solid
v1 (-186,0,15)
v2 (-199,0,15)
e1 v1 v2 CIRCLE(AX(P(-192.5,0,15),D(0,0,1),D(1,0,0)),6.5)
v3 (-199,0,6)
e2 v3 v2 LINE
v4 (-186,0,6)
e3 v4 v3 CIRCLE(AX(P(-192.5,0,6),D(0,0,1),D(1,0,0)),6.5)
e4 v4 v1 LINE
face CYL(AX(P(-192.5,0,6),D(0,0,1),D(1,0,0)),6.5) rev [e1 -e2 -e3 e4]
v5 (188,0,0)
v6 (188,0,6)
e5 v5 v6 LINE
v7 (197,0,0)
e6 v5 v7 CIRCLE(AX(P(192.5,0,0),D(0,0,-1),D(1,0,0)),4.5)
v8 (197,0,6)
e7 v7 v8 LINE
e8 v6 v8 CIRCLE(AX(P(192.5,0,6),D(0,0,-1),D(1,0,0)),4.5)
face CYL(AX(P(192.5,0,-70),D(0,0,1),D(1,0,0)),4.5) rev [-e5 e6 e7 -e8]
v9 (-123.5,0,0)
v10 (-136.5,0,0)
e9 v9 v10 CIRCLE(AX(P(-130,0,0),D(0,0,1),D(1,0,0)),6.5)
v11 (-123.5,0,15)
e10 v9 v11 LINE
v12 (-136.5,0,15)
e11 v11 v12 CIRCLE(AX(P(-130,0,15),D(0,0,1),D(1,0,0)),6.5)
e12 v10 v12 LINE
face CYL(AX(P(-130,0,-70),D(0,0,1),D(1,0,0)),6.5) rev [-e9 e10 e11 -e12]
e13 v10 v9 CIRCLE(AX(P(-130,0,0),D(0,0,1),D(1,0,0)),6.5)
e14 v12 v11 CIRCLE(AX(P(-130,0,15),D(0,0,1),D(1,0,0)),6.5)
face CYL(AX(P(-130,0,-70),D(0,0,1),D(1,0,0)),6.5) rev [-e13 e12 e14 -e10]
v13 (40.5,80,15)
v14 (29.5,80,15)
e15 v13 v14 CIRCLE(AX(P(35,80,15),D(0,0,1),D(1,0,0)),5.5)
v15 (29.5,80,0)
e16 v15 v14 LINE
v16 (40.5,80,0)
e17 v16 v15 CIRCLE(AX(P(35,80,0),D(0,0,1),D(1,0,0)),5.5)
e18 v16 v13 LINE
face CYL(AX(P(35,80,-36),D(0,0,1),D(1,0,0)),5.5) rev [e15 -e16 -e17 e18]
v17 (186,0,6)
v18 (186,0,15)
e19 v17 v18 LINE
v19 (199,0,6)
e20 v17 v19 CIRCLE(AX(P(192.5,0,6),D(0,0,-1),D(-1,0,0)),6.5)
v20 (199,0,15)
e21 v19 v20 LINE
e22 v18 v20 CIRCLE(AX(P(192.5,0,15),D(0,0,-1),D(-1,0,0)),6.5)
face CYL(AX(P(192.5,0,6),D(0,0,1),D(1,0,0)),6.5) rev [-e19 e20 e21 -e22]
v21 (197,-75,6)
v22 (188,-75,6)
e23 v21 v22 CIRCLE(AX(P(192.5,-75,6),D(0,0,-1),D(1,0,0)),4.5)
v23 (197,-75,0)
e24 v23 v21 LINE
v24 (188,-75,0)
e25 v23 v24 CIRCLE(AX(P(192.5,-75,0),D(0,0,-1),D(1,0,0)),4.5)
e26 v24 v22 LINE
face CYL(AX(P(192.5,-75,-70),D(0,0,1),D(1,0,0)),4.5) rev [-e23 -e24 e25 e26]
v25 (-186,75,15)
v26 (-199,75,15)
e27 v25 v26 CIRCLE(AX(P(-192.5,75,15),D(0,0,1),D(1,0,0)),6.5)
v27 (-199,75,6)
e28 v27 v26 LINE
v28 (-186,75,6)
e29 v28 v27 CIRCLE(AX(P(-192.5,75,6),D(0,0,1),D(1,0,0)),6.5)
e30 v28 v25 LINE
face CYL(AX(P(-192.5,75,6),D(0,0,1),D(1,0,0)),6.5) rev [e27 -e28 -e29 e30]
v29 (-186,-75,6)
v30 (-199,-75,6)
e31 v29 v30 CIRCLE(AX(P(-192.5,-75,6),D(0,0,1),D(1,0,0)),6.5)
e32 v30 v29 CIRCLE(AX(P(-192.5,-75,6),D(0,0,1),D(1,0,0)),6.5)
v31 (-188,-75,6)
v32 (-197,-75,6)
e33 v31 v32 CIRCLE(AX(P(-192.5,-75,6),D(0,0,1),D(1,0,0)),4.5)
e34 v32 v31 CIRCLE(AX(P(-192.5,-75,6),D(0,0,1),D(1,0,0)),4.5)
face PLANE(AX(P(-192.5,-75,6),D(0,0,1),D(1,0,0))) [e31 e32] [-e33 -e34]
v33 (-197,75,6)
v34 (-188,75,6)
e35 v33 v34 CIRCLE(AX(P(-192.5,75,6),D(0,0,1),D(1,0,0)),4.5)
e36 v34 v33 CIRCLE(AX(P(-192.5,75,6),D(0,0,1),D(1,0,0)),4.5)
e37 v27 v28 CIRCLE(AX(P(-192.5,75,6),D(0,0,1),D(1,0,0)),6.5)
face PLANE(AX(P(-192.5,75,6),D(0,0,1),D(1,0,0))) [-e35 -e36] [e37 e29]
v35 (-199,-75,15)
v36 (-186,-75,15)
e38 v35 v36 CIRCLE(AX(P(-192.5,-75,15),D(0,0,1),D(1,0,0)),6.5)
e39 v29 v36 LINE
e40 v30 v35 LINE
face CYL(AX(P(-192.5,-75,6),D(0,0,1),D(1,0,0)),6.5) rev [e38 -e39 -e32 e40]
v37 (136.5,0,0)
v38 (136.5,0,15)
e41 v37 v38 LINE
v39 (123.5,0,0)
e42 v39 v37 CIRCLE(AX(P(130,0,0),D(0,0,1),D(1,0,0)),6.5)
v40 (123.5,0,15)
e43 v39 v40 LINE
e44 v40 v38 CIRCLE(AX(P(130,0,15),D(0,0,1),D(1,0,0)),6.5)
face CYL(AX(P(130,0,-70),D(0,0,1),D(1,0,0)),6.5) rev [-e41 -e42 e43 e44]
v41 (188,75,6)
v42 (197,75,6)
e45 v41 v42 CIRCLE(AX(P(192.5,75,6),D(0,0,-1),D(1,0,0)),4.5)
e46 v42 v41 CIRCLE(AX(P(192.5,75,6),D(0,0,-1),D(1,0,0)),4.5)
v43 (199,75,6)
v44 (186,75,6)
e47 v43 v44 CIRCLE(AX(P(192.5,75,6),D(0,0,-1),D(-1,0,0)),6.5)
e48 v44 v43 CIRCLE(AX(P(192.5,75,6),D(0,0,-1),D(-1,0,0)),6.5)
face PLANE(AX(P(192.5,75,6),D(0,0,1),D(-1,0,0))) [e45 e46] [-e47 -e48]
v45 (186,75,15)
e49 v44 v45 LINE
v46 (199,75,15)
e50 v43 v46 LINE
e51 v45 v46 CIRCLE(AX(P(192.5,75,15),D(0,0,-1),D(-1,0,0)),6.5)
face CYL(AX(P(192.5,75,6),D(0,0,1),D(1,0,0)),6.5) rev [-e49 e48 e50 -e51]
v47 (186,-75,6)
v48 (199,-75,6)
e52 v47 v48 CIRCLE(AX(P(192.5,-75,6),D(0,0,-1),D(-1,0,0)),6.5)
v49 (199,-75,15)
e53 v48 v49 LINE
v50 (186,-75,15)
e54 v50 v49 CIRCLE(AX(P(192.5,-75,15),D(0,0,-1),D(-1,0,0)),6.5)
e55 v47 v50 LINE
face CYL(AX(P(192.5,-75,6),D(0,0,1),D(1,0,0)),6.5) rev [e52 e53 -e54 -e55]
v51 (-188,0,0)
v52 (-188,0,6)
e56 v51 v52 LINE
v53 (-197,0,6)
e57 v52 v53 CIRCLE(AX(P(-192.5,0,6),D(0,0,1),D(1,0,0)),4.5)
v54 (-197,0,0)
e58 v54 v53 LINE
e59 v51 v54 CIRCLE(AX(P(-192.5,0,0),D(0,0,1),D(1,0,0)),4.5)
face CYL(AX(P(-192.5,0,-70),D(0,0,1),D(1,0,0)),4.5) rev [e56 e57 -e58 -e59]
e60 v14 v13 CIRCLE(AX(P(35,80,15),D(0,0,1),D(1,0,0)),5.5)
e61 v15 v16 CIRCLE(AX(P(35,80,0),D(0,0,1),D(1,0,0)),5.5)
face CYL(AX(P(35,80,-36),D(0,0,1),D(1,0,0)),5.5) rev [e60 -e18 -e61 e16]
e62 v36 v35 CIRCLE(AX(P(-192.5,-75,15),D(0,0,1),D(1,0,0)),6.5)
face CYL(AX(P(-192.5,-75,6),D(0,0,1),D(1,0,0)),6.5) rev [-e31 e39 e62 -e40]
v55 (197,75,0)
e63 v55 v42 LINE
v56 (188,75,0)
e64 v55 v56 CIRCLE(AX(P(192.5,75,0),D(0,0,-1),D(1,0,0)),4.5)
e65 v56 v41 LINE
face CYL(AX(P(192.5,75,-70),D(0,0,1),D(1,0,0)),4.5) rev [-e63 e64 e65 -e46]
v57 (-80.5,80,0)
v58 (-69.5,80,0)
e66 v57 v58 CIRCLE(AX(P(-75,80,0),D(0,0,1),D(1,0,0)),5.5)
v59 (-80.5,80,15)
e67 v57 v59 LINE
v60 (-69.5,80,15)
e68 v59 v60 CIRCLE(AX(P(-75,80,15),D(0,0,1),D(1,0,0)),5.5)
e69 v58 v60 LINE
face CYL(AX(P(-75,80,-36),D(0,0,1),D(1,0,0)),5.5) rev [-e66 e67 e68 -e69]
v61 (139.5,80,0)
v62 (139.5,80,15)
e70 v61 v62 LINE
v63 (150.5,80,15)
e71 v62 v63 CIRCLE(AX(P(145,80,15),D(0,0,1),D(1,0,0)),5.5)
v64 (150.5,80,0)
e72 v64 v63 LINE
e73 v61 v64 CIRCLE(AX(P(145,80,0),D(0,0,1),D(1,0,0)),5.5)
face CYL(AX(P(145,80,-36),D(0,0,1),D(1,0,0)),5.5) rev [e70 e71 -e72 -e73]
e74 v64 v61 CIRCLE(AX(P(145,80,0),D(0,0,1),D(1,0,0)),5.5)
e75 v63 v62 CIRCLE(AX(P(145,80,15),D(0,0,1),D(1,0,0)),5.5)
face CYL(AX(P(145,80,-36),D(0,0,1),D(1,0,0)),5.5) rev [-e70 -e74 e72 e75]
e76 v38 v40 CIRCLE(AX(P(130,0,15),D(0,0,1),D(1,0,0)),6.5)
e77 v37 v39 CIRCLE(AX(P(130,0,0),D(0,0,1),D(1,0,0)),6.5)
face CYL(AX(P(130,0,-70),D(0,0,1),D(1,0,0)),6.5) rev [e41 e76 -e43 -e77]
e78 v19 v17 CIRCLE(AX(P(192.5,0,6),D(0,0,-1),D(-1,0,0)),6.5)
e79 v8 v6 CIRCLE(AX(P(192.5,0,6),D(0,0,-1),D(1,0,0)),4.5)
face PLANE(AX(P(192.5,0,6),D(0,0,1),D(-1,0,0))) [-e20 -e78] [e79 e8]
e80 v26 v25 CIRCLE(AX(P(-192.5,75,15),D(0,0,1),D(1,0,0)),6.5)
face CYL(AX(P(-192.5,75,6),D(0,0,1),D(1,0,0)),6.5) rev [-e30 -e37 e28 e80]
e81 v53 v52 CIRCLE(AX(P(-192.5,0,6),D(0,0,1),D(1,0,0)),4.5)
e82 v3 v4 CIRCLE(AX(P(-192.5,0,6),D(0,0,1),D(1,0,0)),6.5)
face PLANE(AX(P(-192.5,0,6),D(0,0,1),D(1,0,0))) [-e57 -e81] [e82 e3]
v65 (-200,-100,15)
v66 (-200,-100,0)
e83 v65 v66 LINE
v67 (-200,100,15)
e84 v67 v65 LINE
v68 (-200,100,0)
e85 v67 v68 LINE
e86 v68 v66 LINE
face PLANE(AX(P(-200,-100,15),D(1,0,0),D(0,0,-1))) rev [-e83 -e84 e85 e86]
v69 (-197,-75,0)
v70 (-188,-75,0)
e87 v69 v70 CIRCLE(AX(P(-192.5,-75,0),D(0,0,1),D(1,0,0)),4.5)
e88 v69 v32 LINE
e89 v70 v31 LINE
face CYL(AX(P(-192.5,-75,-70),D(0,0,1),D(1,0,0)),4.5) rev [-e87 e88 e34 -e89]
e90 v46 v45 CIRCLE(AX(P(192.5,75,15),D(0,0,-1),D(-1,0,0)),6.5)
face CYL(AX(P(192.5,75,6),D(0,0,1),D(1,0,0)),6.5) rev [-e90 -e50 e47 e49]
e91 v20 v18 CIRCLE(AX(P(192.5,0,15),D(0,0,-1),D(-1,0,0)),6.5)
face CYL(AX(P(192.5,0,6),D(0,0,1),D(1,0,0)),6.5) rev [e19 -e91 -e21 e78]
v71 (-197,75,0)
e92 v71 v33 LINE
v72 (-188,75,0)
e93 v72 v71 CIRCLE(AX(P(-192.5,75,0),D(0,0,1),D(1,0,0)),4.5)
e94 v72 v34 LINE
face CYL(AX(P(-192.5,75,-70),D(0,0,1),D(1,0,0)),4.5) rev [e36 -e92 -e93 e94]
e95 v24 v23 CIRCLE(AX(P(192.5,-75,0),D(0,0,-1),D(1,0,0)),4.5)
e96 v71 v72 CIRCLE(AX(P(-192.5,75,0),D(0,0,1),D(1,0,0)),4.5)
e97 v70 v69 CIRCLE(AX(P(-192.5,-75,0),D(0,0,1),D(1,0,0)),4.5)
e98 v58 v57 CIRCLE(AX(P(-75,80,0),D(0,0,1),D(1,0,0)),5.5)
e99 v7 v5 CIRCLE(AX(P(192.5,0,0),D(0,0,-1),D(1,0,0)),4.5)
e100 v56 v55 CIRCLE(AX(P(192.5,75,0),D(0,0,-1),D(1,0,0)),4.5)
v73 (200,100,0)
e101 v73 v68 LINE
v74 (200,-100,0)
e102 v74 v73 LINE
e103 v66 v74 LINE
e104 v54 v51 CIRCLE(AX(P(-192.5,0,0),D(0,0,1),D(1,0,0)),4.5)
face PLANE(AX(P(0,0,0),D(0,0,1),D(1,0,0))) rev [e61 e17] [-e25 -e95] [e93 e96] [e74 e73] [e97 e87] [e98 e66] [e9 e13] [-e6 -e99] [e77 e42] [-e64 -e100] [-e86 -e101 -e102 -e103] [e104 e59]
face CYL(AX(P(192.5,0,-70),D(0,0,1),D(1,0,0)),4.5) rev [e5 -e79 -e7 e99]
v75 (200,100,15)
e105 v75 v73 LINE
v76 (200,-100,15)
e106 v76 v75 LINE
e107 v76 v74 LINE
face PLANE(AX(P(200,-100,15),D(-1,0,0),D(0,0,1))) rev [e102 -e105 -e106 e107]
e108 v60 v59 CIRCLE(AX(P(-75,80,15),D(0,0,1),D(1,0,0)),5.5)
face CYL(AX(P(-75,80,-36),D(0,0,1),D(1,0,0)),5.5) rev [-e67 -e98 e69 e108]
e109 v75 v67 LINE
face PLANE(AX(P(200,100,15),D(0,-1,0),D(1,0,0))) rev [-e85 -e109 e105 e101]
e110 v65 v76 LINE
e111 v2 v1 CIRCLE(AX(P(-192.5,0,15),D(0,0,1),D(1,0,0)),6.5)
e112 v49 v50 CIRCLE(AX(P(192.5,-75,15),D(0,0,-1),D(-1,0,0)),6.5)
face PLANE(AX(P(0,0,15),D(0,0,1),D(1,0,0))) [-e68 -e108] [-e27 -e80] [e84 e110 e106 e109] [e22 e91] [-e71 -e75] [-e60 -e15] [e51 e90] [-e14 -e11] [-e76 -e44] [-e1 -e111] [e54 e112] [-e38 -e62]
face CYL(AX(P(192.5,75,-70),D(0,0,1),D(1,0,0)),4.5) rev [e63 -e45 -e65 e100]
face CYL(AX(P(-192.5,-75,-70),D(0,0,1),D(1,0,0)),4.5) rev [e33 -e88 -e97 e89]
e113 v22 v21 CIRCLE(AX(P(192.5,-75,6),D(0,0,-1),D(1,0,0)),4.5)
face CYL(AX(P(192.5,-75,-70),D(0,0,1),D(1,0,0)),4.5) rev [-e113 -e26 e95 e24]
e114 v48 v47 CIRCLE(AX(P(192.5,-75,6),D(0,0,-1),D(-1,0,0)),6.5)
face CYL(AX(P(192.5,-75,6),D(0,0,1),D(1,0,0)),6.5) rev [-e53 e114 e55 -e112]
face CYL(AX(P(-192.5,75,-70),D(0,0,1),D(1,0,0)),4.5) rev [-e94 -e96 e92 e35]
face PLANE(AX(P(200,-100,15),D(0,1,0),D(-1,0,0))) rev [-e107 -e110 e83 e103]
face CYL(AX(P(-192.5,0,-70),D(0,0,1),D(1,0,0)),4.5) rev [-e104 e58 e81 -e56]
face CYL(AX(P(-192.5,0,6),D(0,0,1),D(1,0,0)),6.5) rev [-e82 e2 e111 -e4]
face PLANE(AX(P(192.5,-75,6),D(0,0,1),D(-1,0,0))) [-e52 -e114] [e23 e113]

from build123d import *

# Parameters (mm, degrees)
SKETCH1_W               = 400
SKETCH1_H               = 200
BOSS_EXTRUDE1_DEPTH     = 15
SKETCH2_R               = 6.5
CUT_EXTRUDE1_DEPTH      = 9
LPATTERN1_COUNT         = 3
LPATTERN1_PITCH         = 75
MIRROR1_COPY_1_SKETCH_R = 6.5
MIRROR1_COPY_1_DEPTH    = 9
MIRROR1_COPY_2_SKETCH_R = 6.5
MIRROR1_COPY_2_DEPTH    = 9
SKETCH3_R               = 4.5
CUT_EXTRUDE2_DEPTH      = 85
LPATTERN2_COUNT         = 3
LPATTERN2_PITCH         = 75
MIRROR2_COPY_1_SKETCH_R = 4.5
MIRROR2_COPY_1_DEPTH    = 85
MIRROR2_COPY_2_SKETCH_R = 4.5
MIRROR2_COPY_2_DEPTH    = 85
SKETCH4_R               = 6.5
CUT_EXTRUDE3_DEPTH      = 85
LPATTERN3_COUNT         = 3
LPATTERN3_PITCH         = 130
SKETCH5_R               = 5.5
CUT_EXTRUDE4_DEPTH      = 51
LPATTERN4_COUNT         = 3
LPATTERN4_PITCH         = 110


with BuildPart() as part:
    # Sketch1 → Boss-Extrude1 (new body)
    with BuildSketch(Plane.XY):
        Rectangle(SKETCH1_W, SKETCH1_H)
    extrude(amount=BOSS_EXTRUDE1_DEPTH)

    # Sketch2 → Cut-Extrude1 (cut)
    with BuildSketch(Plane.XY.offset(15)):
        with Locations((-192.5, 75)):
            Circle(SKETCH2_R)
    cut_extrude1 = extrude(amount=-CUT_EXTRUDE1_DEPTH, mode=Mode.SUBTRACT)

    # LPattern1: Cut-Extrude1 ×3
    with Locations(*[(0, -i * LPATTERN1_PITCH, 0) for i in range(1, LPATTERN1_COUNT)]):
        add(cut_extrude1, mode=Mode.SUBTRACT)

    # Mirror1: Cut-Extrude1 across plane
    add(cut_extrude1.mirror(Plane(origin=(0, 0, 0), x_dir=(0, 0, 1), z_dir=(1, 0, 0))), mode=Mode.SUBTRACT)

    # Mirror1 copy 1 sketch → Mirror1 copy 1 (cut)
    with BuildSketch(Plane(origin=(0, -75, 15), x_dir=(-1, 0, 0), z_dir=(0, 0, 1))):
        with Locations((-192.5, -75)):
            Circle(MIRROR1_COPY_1_SKETCH_R)
    extrude(amount=-MIRROR1_COPY_1_DEPTH, mode=Mode.SUBTRACT)

    # Mirror1 copy 2 sketch → Mirror1 copy 2 (cut)
    with BuildSketch(Plane(origin=(0, -150, 15), x_dir=(-1, 0, 0), z_dir=(0, 0, 1))):
        with Locations((-192.5, -75)):
            Circle(MIRROR1_COPY_2_SKETCH_R)
    extrude(amount=-MIRROR1_COPY_2_DEPTH, mode=Mode.SUBTRACT)

    # Sketch3 → Cut-Extrude2 (cut)
    with BuildSketch(Plane.XY.offset(15)):
        with Locations((-192.5, 75)):
            Circle(SKETCH3_R)
    cut_extrude2 = extrude(amount=-CUT_EXTRUDE2_DEPTH, mode=Mode.SUBTRACT)

    # LPattern2: Cut-Extrude2 ×3
    with Locations(*[(0, -i * LPATTERN2_PITCH, 0) for i in range(1, LPATTERN2_COUNT)]):
        add(cut_extrude2, mode=Mode.SUBTRACT)

    # Mirror2: Cut-Extrude2 across plane
    add(cut_extrude2.mirror(Plane(origin=(0, 0, 0), x_dir=(0, 0, 1), z_dir=(1, 0, 0))), mode=Mode.SUBTRACT)

    # Mirror2 copy 1 sketch → Mirror2 copy 1 (cut)
    with BuildSketch(Plane(origin=(0, -75, 15), x_dir=(-1, 0, 0), z_dir=(0, 0, 1))):
        with Locations((-192.5, -75)):
            Circle(MIRROR2_COPY_1_SKETCH_R)
    extrude(amount=-MIRROR2_COPY_1_DEPTH, mode=Mode.SUBTRACT)

    # Mirror2 copy 2 sketch → Mirror2 copy 2 (cut)
    with BuildSketch(Plane(origin=(0, -150, 15), x_dir=(-1, 0, 0), z_dir=(0, 0, 1))):
        with Locations((-192.5, -75)):
            Circle(MIRROR2_COPY_2_SKETCH_R)
    extrude(amount=-MIRROR2_COPY_2_DEPTH, mode=Mode.SUBTRACT)

    # Sketch4 → Cut-Extrude3 (cut)
    with BuildSketch(Plane.XY.offset(15)):
        with Locations((-130, 0)):
            Circle(SKETCH4_R)
    cut_extrude3 = extrude(amount=-CUT_EXTRUDE3_DEPTH, mode=Mode.SUBTRACT)

    # LPattern3: Cut-Extrude3 ×3, 1 skipped
    with Locations(*[(i * LPATTERN3_PITCH, 0, 0) for i in range(1, LPATTERN3_COUNT) if i not in (1,)]):
        add(cut_extrude3, mode=Mode.SUBTRACT)

    # Sketch5 → Cut-Extrude4 (cut)
    with BuildSketch(Plane.XY.offset(15)):
        with Locations((-75, 80)):
            Circle(SKETCH5_R)
    cut_extrude4 = extrude(amount=-CUT_EXTRUDE4_DEPTH, mode=Mode.SUBTRACT)

    # LPattern4: Cut-Extrude4 ×3
    with Locations(*[(i * LPATTERN4_PITCH, 0, 0) for i in range(1, LPATTERN4_COUNT)]):
        add(cut_extrude4, mode=Mode.SUBTRACT)


solid = part.part
